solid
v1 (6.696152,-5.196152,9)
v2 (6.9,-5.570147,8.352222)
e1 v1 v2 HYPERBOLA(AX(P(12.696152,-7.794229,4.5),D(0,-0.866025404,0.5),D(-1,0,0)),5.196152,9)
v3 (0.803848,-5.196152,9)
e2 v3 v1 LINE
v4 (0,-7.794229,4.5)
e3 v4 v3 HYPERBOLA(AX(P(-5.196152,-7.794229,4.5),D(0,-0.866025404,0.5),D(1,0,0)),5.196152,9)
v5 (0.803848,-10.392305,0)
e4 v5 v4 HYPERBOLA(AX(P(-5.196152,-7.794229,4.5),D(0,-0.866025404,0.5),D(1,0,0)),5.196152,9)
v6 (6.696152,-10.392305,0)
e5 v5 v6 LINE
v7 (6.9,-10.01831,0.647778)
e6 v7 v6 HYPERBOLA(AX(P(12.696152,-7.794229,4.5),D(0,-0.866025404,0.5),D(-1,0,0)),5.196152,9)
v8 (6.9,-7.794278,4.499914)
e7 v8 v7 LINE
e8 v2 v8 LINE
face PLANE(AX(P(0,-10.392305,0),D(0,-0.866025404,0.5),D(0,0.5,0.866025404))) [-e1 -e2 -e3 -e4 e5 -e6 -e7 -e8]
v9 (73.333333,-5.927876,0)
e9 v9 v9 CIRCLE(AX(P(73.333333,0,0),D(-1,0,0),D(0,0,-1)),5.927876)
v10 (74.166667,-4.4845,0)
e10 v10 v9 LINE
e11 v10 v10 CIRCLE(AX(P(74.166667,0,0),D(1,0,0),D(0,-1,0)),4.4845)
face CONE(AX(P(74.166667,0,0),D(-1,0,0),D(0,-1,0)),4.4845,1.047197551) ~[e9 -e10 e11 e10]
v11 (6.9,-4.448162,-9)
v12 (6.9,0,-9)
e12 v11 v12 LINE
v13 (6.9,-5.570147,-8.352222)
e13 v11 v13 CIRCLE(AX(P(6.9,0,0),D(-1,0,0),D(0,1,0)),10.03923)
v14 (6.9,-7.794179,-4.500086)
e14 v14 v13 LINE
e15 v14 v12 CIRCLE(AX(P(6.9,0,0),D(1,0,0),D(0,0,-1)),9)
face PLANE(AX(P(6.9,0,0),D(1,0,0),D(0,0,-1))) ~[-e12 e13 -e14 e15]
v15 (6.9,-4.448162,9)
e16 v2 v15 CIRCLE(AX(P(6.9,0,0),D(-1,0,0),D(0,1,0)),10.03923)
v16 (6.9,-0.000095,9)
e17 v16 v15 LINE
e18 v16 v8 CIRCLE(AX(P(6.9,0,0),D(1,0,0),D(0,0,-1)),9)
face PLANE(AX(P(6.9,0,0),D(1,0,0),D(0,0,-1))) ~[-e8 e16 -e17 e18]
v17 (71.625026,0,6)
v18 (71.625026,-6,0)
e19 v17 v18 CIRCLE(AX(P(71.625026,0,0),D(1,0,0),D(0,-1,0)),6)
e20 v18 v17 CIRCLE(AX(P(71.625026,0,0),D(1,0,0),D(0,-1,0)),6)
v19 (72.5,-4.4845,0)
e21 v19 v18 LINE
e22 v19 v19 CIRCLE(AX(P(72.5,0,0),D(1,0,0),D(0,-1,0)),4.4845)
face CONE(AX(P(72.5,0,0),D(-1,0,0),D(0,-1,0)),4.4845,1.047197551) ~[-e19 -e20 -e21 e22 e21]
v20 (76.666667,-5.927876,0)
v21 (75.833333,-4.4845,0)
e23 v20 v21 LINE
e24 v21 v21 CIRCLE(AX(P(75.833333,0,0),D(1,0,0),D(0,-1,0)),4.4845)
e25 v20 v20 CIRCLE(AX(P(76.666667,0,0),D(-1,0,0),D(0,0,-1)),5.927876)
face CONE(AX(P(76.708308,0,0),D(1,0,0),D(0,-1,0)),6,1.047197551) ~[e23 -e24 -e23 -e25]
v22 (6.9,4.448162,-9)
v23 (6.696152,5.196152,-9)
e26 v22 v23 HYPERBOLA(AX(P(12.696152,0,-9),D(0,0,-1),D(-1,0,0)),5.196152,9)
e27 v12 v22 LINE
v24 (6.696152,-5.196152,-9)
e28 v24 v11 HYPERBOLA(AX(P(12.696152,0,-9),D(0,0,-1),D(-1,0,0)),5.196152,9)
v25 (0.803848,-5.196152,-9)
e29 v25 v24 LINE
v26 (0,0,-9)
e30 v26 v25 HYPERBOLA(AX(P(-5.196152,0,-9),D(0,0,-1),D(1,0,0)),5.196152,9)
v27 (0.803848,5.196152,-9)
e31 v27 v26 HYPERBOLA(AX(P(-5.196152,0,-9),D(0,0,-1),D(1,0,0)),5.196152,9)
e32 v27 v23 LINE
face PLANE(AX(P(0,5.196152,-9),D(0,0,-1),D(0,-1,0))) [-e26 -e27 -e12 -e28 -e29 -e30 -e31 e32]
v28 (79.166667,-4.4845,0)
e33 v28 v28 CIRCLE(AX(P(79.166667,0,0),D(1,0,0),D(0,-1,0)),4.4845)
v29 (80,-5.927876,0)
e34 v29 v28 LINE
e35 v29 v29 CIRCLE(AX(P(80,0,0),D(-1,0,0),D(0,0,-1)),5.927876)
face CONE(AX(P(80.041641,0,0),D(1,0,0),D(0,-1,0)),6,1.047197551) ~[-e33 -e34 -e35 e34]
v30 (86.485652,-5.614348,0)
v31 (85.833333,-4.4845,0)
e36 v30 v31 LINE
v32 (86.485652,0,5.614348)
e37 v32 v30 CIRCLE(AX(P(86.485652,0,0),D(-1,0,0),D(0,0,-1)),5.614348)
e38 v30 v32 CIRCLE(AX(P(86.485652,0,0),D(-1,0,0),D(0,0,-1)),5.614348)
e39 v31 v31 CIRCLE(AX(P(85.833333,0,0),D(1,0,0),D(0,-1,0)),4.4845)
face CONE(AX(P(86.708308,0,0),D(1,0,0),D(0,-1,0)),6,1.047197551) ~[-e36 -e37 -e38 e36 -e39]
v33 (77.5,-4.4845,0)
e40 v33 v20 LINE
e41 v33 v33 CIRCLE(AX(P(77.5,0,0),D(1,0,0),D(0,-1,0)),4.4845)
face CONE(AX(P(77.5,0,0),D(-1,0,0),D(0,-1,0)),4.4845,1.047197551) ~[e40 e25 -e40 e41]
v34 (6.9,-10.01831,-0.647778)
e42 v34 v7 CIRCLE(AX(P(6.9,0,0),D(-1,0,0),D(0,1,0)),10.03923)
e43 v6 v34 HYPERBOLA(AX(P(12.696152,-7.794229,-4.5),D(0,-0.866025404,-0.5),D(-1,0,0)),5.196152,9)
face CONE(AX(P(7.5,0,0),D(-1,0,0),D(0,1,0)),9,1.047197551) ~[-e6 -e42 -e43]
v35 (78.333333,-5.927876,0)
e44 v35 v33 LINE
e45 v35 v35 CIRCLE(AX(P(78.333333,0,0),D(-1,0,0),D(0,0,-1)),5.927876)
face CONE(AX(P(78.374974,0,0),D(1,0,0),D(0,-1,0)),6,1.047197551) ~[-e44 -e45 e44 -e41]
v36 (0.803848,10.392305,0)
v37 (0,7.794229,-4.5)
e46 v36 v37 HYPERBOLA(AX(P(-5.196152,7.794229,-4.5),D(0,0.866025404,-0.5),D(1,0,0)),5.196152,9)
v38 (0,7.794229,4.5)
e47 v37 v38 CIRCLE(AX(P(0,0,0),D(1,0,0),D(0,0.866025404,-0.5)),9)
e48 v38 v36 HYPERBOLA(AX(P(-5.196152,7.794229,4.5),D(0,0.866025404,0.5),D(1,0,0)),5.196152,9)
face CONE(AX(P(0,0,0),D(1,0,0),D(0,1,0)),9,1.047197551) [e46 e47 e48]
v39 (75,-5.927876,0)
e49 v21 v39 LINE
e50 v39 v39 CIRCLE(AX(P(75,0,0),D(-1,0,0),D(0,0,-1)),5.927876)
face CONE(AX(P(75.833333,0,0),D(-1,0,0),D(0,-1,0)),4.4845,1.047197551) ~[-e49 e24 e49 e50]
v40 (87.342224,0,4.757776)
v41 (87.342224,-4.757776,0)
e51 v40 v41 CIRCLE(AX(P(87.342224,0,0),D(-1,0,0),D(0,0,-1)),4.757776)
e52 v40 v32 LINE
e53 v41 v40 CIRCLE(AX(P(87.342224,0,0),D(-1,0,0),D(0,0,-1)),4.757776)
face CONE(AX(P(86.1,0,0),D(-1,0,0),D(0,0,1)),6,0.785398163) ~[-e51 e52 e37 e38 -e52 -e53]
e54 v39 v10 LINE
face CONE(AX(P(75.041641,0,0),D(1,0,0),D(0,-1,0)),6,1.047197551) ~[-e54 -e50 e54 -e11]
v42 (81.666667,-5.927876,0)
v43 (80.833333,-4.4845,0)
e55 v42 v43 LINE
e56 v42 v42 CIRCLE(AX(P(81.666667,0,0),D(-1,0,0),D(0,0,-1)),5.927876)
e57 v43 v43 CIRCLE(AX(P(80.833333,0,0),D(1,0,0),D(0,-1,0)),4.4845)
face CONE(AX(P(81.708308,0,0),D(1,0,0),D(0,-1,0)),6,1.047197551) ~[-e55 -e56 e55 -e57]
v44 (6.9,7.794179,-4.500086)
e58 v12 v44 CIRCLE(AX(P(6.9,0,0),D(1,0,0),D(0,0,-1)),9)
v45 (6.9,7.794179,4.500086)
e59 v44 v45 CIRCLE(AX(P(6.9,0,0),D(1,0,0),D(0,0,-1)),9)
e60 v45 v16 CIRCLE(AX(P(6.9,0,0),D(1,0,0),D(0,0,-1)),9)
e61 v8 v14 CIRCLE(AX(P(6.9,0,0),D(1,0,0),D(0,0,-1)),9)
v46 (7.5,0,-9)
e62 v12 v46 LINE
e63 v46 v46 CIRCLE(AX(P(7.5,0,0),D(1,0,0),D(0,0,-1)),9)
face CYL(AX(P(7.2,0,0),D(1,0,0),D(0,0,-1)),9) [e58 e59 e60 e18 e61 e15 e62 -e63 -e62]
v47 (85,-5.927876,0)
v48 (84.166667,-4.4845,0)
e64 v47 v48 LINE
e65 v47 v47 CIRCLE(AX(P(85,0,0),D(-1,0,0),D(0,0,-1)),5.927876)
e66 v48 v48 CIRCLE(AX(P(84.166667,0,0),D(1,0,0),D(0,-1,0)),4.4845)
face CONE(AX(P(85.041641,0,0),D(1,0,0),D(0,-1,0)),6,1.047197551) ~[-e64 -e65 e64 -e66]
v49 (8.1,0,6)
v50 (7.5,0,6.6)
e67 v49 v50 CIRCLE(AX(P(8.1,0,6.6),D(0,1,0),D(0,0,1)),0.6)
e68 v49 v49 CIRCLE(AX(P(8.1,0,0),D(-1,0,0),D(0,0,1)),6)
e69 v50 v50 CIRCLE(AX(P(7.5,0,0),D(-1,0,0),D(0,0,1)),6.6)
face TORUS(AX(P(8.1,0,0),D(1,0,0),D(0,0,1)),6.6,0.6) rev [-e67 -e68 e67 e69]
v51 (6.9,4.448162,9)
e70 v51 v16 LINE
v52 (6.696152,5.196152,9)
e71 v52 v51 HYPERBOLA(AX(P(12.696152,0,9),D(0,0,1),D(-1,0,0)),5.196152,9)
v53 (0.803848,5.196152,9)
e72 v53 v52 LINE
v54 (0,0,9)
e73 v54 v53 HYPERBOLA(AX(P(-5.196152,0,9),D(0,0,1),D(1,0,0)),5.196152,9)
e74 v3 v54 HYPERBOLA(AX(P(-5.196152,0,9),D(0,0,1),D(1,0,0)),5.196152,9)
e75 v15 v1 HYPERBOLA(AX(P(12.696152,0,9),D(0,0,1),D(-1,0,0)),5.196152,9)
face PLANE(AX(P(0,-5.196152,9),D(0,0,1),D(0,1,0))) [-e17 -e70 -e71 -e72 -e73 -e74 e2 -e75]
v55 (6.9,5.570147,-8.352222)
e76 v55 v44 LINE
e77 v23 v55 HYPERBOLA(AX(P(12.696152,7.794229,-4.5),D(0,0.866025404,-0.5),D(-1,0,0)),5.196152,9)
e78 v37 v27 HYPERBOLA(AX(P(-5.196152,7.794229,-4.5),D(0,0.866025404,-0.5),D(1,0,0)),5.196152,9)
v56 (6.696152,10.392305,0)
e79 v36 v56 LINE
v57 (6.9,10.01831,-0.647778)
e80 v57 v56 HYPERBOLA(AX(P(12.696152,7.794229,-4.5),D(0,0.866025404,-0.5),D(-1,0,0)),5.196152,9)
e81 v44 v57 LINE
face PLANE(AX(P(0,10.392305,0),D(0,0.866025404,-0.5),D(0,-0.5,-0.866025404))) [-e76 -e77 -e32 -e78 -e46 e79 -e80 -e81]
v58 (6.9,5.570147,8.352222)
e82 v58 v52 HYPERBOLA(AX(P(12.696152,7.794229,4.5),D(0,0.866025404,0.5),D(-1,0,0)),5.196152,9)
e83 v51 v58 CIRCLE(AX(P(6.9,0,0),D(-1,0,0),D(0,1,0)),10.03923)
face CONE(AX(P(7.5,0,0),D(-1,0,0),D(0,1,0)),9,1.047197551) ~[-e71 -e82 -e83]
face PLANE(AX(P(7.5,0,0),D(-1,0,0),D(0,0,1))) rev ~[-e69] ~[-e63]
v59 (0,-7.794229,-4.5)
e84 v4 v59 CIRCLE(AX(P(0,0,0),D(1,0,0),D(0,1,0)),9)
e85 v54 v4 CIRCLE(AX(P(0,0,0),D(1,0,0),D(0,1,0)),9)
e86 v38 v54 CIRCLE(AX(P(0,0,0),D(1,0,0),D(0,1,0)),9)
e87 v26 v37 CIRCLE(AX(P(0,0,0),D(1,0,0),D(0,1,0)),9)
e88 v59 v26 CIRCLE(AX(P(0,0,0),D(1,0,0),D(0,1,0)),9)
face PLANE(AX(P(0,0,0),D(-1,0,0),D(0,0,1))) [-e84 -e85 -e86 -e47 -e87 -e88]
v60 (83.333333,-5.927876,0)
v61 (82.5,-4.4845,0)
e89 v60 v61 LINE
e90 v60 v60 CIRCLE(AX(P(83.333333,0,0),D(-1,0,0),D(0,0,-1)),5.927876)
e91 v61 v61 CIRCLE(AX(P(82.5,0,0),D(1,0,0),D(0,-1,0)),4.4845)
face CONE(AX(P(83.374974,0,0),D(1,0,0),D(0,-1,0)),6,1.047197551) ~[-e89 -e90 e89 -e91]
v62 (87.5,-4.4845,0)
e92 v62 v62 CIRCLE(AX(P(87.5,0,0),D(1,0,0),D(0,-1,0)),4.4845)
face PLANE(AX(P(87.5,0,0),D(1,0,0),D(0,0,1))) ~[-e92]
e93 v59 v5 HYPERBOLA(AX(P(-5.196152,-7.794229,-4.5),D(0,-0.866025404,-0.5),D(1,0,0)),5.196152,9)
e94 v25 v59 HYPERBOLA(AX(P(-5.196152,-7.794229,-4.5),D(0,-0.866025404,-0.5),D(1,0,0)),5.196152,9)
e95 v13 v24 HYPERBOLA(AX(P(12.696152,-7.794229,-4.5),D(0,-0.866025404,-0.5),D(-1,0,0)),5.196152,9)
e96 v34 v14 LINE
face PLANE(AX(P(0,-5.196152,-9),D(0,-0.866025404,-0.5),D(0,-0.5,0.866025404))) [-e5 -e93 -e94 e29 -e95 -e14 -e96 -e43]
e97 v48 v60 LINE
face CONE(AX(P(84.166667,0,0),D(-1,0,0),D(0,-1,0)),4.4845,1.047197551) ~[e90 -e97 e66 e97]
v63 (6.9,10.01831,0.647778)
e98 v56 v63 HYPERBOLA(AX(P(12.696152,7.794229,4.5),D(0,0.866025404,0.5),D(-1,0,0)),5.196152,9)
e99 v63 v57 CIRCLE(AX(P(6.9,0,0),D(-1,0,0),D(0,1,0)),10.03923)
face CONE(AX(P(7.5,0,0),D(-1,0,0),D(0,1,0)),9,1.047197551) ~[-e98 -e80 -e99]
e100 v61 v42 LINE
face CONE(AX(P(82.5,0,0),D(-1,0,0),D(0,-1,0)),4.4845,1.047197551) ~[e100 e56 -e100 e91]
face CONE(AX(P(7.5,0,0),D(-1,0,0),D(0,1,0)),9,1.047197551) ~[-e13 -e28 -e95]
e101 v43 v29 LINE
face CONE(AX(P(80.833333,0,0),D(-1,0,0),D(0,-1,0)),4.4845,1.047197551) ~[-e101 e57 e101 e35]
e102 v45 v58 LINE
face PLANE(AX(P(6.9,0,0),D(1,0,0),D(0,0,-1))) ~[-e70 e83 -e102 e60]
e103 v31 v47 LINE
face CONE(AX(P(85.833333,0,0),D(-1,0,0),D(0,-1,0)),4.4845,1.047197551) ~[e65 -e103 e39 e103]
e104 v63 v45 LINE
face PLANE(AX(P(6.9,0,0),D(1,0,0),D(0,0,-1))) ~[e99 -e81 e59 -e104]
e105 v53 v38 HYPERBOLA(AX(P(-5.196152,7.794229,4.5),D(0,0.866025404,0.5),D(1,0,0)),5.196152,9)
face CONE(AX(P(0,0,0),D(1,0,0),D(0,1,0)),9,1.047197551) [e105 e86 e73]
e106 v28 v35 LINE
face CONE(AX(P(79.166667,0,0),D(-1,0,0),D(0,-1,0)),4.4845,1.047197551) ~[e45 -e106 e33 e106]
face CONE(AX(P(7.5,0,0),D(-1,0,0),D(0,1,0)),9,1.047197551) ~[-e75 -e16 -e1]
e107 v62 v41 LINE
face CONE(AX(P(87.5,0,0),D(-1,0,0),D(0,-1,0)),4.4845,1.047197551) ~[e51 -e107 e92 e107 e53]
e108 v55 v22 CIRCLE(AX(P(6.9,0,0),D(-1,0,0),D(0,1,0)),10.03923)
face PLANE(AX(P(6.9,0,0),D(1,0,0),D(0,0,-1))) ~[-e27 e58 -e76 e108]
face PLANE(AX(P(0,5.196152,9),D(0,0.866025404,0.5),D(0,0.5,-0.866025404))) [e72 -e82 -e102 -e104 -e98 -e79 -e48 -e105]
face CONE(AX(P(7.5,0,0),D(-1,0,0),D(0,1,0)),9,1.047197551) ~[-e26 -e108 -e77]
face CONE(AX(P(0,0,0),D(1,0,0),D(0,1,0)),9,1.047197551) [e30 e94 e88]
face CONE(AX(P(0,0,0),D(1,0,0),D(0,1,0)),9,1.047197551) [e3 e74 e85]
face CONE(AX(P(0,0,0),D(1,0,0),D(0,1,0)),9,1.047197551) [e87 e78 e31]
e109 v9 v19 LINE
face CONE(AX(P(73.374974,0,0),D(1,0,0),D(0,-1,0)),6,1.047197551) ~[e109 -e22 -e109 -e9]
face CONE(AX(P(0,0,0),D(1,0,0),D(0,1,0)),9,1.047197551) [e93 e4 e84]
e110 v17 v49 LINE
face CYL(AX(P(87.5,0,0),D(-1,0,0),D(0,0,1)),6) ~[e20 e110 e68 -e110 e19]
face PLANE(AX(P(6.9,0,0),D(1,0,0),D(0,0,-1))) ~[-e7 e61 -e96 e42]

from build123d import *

# Parameters (mm, degrees)
EXTRUDE_364_DEPTH      = 7.5
SKETCH_4_W             = 0.6
SKETCH_4_H             = 11.392304845
CHAMFER_2049_SIZE      = 1.4
FILLET_2094_R          = 0.6
PATTERN_LINEAR_1_COUNT = 10
PATTERN_LINEAR_1_PITCH = 1.666666667


with BuildPart() as part:
    # 草图1 → Extrude 364 (new body)
    with BuildSketch(Plane(origin=(0, 0, 0), x_dir=(0, 0, -1), z_dir=(1, 0, 0))):
        Polygon((9, 5.196152423), (9, -5.196152423), (0, -10.392304845), (-9, -5.196152423), (-9, 5.196152423), (0, 10.392304845), align=None)
    extrude(amount=EXTRUDE_364_DEPTH)

    # 草图2 → 凸台-旋转1 (revolve)
    with BuildSketch(Plane.XY, mode=Mode.PRIVATE) as revolve_1_sk:
        Polygon((0, 0), (87.5, 0), (87.5, 4.4845), (87.5, 6), (7.791693541, 6), (0, 6), align=None)
    revolve(revolve_1_sk.sketch.rotate(Axis((0, 0, 0), (1, 0, 0)), 90), axis=Axis((0, 0, 0), (1, 0, 0)))

    # 草图3 → 切除-旋转1 (revolve, cut)
    with BuildSketch(Plane.XY):
        Polygon((0, 9), (3.690598923, 15.392304845), (3.690598923, 20.392304845), (-10, 20.392304845), (-10, 9), align=None)
    revolve(axis=Axis((0, 0, 0), (1, 0, 0)), mode=Mode.SUBTRACT)

    # 草图5 → 切除-旋转2 (revolve, cut)
    with BuildSketch(Plane.XY):
        Polygon((7.5, 9), (3.809401077, 15.392304845), (3.809401077, 20.392304845), (13.809401077, 20.392304845), (13.809401077, 9), align=None)
    revolve(axis=Axis((0, 0, 0), (1, 0, 0)), mode=Mode.SUBTRACT)

    # 草图4 → 切除-旋转3 (revolve, cut)
    with BuildSketch(Plane.XY, mode=Mode.PRIVATE) as cut_revolve_3_sk:
        with Locations((7.2, 14.696152423)):
            Rectangle(SKETCH_4_W, SKETCH_4_H)
    revolve(cut_revolve_3_sk.sketch.rotate(Axis((0, 0, 0), (1, 0, 0)), 270), axis=Axis((0, 0, 0), (1, 0, 0)), mode=Mode.SUBTRACT)

    # Chamfer 2049
    chamfer_2049_edges = [part.edges().sort_by_distance(p)[0] for p in [
        (87.5, 0, -6),
    ]]
    chamfer(chamfer_2049_edges, length=CHAMFER_2049_SIZE)

    # Fillet 2094
    fillet_2094_edges = [part.edges().sort_by_distance(p)[0] for p in [
        (7.5, 0, -6),
    ]]
    fillet(fillet_2094_edges, radius=FILLET_2094_R)

    # 草图6 → 切除-旋转4 (revolve, cut)
    with BuildSketch(Plane.XY):
        Polygon((72.5, -4.4845), (71.625025667, -6), (71.625025667, -7.5), (73.374974333, -7.5), (73.374974333, -6), align=None)
    cut_revolve_4 = revolve(axis=Axis((-3.175, 0, 0), (1, 0, 0)), mode=Mode.SUBTRACT)

    # 阵列(线性)1: 切除-旋转4 ×10
    with Locations(*[(i * PATTERN_LINEAR_1_PITCH, 0, 0) for i in range(1, PATTERN_LINEAR_1_COUNT)]):
        add(cut_revolve_4, mode=Mode.SUBTRACT)


solid = part.part
